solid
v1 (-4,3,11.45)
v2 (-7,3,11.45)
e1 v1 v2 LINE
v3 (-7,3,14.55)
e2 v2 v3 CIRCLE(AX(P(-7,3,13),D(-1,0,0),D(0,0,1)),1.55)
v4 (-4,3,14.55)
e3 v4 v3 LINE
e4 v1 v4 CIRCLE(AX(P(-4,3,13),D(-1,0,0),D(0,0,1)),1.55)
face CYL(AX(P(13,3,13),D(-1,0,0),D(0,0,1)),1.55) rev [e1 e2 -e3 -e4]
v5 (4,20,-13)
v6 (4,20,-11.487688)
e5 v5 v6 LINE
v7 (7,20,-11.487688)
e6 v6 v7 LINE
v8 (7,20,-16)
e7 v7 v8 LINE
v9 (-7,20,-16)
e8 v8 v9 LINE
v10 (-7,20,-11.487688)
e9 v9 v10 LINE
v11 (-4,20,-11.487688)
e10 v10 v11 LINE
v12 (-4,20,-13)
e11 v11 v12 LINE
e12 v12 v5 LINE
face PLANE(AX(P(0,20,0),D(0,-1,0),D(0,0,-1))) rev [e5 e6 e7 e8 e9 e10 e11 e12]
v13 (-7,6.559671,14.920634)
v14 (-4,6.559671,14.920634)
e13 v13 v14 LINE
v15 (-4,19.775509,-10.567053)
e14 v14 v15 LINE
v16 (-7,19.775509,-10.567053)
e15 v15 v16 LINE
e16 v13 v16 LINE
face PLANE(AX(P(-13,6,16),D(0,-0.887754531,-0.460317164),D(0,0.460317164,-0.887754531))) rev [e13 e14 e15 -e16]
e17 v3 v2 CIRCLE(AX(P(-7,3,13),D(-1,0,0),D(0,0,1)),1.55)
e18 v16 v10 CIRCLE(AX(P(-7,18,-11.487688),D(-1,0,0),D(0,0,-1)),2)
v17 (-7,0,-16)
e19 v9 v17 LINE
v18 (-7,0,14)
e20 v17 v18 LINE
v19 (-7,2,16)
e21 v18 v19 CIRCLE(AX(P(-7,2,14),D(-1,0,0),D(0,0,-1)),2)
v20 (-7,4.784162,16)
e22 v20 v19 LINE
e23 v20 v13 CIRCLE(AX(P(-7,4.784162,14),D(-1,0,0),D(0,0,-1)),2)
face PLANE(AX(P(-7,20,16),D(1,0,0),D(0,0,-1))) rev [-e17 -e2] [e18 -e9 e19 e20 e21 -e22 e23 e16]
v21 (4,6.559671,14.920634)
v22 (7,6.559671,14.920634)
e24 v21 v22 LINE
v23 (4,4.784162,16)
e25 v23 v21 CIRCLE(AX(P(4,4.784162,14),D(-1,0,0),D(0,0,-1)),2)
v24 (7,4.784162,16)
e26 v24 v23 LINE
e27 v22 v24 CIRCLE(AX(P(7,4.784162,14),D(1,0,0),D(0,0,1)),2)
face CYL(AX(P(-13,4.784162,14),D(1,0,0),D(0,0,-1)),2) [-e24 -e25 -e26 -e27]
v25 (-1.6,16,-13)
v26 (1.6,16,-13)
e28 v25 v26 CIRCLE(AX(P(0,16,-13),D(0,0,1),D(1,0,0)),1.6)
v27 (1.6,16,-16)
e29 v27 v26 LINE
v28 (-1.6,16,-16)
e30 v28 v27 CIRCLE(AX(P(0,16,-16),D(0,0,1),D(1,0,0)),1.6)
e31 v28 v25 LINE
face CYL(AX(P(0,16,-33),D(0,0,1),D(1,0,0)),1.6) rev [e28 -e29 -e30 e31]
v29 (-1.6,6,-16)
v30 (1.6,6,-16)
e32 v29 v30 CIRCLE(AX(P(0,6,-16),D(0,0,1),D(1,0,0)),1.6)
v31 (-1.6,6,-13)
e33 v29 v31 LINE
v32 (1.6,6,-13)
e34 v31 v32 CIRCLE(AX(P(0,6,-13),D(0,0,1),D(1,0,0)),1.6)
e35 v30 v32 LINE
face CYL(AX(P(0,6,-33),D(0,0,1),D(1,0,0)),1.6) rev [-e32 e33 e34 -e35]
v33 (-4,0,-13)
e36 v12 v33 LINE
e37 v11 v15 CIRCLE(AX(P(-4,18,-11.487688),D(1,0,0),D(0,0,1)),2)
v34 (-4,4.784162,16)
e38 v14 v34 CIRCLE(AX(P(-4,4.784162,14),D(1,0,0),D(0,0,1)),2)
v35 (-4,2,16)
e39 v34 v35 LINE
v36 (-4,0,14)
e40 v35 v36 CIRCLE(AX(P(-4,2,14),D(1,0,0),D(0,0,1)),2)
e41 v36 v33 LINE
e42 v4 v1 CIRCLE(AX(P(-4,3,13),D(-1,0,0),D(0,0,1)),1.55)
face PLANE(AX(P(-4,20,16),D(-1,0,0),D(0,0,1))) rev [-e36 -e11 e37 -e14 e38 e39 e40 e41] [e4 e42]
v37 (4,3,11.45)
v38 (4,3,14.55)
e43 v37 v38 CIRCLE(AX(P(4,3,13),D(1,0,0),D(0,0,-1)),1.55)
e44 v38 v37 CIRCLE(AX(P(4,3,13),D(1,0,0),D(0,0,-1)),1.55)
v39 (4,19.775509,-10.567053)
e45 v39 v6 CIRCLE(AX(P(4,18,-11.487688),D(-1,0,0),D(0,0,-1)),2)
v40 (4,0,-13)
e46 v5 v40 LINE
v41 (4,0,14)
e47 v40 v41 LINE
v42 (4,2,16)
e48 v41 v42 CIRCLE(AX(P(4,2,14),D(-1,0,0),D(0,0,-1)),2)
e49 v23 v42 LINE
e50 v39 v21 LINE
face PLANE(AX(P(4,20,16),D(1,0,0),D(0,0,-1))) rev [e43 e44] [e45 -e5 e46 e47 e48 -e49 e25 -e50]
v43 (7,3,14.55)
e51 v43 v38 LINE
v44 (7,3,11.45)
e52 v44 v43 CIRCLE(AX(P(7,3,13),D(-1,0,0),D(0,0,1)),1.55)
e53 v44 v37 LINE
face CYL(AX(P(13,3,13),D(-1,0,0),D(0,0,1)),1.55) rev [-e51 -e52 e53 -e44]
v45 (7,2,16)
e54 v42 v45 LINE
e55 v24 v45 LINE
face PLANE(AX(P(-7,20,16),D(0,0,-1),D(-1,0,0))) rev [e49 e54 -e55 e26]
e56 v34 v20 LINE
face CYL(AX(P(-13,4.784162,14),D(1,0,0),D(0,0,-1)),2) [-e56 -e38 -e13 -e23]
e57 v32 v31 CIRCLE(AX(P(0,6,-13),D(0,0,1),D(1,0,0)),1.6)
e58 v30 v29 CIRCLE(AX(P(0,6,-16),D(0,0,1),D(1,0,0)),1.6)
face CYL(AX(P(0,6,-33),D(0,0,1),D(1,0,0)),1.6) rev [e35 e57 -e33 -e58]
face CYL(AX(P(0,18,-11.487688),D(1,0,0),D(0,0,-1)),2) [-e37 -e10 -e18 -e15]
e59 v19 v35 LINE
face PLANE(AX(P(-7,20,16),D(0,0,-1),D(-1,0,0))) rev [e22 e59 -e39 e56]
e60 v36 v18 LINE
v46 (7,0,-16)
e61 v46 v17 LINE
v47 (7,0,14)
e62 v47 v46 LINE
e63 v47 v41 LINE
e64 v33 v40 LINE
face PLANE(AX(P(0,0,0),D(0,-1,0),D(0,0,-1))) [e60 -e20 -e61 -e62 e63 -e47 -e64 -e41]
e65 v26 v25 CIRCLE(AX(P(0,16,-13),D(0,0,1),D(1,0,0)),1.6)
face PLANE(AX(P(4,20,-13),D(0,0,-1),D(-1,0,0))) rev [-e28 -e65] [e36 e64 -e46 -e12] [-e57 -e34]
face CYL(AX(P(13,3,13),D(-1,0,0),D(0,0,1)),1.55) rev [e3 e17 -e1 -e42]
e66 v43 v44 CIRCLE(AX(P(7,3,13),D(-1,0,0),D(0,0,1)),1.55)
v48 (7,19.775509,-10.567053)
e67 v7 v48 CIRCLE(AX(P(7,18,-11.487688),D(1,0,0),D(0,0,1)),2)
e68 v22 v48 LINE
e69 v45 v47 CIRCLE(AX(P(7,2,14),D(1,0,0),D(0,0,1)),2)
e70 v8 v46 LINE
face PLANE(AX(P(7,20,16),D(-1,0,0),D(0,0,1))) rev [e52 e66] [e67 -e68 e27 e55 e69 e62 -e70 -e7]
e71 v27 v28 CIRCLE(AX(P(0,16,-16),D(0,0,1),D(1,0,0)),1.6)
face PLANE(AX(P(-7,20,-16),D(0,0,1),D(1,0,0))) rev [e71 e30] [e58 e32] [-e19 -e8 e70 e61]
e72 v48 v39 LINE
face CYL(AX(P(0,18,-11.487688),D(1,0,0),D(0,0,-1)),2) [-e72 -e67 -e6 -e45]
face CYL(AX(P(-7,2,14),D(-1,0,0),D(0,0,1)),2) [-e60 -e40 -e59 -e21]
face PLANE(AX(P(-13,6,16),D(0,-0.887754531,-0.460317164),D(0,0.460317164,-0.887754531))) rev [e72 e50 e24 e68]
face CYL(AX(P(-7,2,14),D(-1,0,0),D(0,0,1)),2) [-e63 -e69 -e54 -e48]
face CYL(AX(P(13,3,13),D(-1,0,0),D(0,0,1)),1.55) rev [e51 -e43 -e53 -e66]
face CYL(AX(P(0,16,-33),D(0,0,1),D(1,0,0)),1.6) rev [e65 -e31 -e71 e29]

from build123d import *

# Parameters (mm, degrees)
SKETCH_1_W          = 14
SKETCH_1_H          = 32
EXTRUDE_1_DEPTH     = 20
CUT_EXTRUDE_1_DEPTH = 20
SKETCH_3_W          = 8
SKETCH_3_H          = 29
CUT_EXTRUDE_2_DEPTH = 20
FILLET_2_R          = 2
SKETCH_4_R          = 1.55
CUT_EXTRUDE_3_DEPTH = 20
SKETCH_5_R          = 1.6
CUT_EXTRUDE_4_DEPTH = 20


with BuildPart() as part:
    # 草图1 → 凸台-拉伸1 (new body)
    with BuildSketch(Plane(origin=(0, 0, 0), x_dir=(1, 0, 0), z_dir=(0, 1, 0))):
        Rectangle(SKETCH_1_W, SKETCH_1_H)
    extrude(amount=EXTRUDE_1_DEPTH)

    # 草图2 → 切除-拉伸1 (cut)
    with BuildSketch(Plane(origin=(7, 0, 0), x_dir=(0, 0, -1), z_dir=(1, 0, 0))):
        Polygon((-16, 6), (11, 20), (-16, 20), align=None)
    extrude(amount=-CUT_EXTRUDE_1_DEPTH, mode=Mode.SUBTRACT)

    # 草图3 → 切除-拉伸2 (cut)
    with BuildSketch(Plane.XZ):
        with Locations((0, 1.5)):
            Rectangle(SKETCH_3_W, SKETCH_3_H)
    extrude(amount=-CUT_EXTRUDE_2_DEPTH, mode=Mode.SUBTRACT)

    # 圆角2
    fillet_2_edges = [part.edges().sort_by_distance(p)[0] for p in [
        (-5.5, 20, -11),
        (-5.5, 6, 16),
        (5.5, 6, 16),
        (5.5, 20, -11),
        (5.5, 0, 16),
        (-5.5, 0, 16),
    ]]
    fillet(fillet_2_edges, radius=FILLET_2_R)

    # 草图4 → 切除-拉伸3 (cut)
    with BuildSketch(Plane.ZY.offset(7)):
        with Locations((13, 3)):
            Circle(SKETCH_4_R)
    extrude(amount=-CUT_EXTRUDE_3_DEPTH, mode=Mode.SUBTRACT)

    # 草图5 → 切除-拉伸4 (cut)
    with BuildSketch(Plane.XY.offset(-13)):
        with Locations((0, 16)):
            Circle(SKETCH_5_R)
        with Locations((0, 6)):
            Circle(SKETCH_5_R)
    extrude(amount=-CUT_EXTRUDE_4_DEPTH, mode=Mode.SUBTRACT)


solid = part.part
